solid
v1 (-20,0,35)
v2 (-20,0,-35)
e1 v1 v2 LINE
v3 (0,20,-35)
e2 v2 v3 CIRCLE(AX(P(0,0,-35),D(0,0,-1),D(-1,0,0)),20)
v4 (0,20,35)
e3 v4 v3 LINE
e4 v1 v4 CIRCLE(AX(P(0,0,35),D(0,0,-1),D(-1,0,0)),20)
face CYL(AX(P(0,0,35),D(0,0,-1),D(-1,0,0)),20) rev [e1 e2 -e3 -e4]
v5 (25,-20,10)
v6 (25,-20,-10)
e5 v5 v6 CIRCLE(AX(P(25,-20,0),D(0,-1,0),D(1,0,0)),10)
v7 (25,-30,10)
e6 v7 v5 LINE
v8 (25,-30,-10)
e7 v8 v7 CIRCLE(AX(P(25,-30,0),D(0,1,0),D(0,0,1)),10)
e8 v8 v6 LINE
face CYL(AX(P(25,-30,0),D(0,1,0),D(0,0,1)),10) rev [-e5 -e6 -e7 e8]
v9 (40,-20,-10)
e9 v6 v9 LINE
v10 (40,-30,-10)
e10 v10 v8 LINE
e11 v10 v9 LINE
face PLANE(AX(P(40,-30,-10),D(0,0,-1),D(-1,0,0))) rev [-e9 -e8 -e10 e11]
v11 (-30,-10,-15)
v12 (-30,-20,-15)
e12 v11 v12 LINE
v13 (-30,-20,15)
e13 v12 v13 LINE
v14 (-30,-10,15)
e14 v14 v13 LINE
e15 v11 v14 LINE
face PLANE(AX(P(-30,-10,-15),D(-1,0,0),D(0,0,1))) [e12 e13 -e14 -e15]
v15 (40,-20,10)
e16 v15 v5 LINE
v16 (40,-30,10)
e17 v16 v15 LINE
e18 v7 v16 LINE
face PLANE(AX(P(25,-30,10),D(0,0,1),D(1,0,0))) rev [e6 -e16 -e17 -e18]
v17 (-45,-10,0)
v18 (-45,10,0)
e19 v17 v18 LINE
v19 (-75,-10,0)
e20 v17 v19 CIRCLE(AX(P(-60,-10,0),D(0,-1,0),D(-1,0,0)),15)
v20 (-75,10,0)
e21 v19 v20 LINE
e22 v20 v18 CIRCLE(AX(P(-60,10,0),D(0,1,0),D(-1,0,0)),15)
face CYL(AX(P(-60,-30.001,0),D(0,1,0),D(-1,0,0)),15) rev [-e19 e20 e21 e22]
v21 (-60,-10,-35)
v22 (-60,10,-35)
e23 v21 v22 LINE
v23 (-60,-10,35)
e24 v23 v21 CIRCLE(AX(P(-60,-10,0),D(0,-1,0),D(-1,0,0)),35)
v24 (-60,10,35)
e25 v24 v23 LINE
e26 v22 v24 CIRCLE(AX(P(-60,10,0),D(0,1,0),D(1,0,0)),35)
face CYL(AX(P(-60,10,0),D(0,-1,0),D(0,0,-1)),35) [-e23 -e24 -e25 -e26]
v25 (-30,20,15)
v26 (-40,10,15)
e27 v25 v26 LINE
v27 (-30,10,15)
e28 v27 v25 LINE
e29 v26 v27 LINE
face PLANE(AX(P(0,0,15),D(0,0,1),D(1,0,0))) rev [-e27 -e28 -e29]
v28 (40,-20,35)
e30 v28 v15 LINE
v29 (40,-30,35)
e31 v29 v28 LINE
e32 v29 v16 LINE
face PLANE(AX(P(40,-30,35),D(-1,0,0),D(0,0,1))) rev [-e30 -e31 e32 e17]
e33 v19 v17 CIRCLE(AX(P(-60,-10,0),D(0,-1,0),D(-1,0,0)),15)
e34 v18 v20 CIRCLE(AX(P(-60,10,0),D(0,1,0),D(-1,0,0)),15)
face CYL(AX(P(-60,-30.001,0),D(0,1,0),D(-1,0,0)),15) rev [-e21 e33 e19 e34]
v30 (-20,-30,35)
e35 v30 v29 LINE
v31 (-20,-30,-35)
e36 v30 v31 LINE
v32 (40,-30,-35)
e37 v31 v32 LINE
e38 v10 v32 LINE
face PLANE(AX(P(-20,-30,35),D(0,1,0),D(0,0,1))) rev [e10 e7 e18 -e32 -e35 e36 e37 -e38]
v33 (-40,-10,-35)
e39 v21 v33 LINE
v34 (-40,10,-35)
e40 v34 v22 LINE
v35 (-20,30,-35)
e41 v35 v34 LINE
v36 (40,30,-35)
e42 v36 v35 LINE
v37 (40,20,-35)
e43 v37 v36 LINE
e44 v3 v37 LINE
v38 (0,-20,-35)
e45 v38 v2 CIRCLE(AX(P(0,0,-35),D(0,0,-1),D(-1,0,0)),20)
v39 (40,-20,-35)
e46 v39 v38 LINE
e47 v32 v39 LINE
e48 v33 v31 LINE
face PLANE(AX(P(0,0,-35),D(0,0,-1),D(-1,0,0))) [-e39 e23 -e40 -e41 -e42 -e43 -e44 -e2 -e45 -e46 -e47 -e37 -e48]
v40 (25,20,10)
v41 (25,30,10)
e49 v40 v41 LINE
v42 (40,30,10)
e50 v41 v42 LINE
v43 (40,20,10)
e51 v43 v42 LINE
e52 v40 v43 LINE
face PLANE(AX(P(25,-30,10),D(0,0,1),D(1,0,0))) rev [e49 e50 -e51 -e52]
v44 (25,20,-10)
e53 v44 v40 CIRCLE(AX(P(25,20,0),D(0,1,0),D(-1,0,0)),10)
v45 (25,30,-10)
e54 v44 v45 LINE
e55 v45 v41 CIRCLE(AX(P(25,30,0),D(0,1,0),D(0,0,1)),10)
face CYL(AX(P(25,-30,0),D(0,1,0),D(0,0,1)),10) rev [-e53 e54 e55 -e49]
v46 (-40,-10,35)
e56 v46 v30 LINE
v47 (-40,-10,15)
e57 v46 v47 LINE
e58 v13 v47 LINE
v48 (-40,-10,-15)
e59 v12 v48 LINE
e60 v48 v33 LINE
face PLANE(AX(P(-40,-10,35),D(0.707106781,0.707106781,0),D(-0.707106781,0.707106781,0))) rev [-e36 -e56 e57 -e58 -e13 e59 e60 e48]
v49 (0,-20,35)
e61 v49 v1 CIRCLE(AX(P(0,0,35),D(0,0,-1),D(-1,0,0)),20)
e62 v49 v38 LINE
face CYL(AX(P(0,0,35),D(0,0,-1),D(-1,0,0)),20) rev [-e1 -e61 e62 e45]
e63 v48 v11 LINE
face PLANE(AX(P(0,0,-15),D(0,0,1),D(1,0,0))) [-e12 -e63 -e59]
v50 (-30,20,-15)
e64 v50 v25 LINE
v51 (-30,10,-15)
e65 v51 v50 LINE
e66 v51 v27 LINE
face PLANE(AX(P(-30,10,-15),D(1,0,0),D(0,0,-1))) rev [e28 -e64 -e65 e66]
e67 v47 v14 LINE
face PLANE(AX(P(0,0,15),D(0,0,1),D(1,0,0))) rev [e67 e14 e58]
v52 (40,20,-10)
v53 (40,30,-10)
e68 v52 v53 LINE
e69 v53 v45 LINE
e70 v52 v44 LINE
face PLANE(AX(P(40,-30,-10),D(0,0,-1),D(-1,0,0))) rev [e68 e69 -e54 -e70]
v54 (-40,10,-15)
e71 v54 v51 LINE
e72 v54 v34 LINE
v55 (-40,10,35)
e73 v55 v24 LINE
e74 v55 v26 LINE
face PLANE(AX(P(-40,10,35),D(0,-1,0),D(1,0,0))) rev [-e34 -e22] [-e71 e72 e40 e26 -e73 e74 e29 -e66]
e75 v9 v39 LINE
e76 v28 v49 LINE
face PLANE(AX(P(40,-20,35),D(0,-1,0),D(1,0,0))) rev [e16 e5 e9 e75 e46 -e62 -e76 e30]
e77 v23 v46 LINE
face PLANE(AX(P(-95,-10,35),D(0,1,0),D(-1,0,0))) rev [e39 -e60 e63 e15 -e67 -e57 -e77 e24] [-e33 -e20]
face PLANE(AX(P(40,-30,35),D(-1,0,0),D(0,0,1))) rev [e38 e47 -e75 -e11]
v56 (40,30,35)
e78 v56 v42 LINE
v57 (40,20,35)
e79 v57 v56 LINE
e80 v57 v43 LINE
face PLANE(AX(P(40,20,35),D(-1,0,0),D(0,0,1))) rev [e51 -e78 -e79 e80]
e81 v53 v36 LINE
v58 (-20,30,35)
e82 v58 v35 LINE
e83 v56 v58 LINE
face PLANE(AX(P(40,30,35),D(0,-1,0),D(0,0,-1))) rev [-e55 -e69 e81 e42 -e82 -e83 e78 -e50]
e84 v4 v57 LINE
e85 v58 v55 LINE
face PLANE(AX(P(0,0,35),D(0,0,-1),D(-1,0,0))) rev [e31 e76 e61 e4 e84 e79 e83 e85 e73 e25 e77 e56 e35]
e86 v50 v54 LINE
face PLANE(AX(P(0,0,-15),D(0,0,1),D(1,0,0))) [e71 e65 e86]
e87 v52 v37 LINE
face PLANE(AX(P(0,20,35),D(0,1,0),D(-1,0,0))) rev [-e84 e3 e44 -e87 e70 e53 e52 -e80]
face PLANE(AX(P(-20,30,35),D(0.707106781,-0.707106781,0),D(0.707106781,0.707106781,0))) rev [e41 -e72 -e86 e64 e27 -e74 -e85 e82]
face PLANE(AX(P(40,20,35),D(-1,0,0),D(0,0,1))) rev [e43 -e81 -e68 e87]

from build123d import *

# Parameters (mm, degrees)
BRACKET_BODY_DEPTH      = 35
EYE_END_ROUND_RADIUS    = 35
EYE_END_ROUND_LENGTH    = 20
FORK_GAP_CUT_DEPTH      = 106.59356041
FORK_GAP_CUT_DEPTH_BACK = 106.59356041
FORK_SLOT_CUT_DEPTH     = 15
EYE_BORE_30_REACH       = 110.858
EYE_BORE_SKETCH_R       = 15


with BuildPart() as part:
    # Bracket Profile Sketch → Bracket Body (new, symmetric)
    with BuildSketch(Plane.XY):
        with BuildLine():
            Line((40, -20), (0, -20))
            ThreePointArc((0, -20), (-20, 0), (0, 20))
            Line((0, 20), (40, 20))
            Line((40, 20), (40, 30))
            Line((40, 30), (-20, 30))
            Line((-20, 30), (-40, 10))
            Line((-40, 10), (-95, 10))
            Line((-95, 10), (-95, -10))
            Line((-95, -10), (-40, -10))
            Line((-40, -10), (-20, -30))
            Line((-20, -30), (40, -30))
            Line((40, -30), (40, -20))
        make_face()
    extrude(amount=BRACKET_BODY_DEPTH, both=True)

    # Eye End Round: full round fillet: the end face becomes a half cylinder, R = half its width
    eye_end_round_face = Plane((-95, 0, 0), x_dir=(0, -1, 0), z_dir=(-1, 0, 0))  # on the end face: x along it, z out of the body
    eye_end_round_slab = eye_end_round_face.offset(-EYE_END_ROUND_RADIUS / 2) * Box(EYE_END_ROUND_LENGTH, 2 * EYE_END_ROUND_RADIUS, EYE_END_ROUND_RADIUS, mode=Mode.PRIVATE)  # the body's end, R deep
    eye_end_round_round = Plane((-60, 0, 0), x_dir=(-1, 0, 0), z_dir=(0, -1, 0)) * Cylinder(EYE_END_ROUND_RADIUS, EYE_END_ROUND_LENGTH, mode=Mode.PRIVATE)  # its axis R under the face
    add(eye_end_round_slab - eye_end_round_round, mode=Mode.SUBTRACT)

    # Fork Gap Sketch → Fork Gap Cut (cut, two sides: drawn at the far end of the back side and taken through both)
    with BuildSketch(Plane(origin=(0, 0, 0), x_dir=(1, 0, 0), z_dir=(0, 1, 0)).offset(-FORK_GAP_CUT_DEPTH_BACK)):
        with BuildLine():
            Line((40, 10), (25, 10))
            ThreePointArc((25, 10), (15, 0), (25, -10))
            Line((25, -10), (40, -10))
            Line((40, -10), (40, 10))
        make_face()
    extrude(amount=FORK_GAP_CUT_DEPTH + FORK_GAP_CUT_DEPTH_BACK, mode=Mode.SUBTRACT)

    # Fork Slot Sketch → Fork Slot Cut (cut, symmetric)
    with BuildSketch(Plane.XY):
        Polygon((-40, 10), (-30, 10), (-30, 20), align=None)
    fork_slot_cut = extrude(amount=FORK_SLOT_CUT_DEPTH, both=True, mode=Mode.SUBTRACT)

    # Eye Bore Sketch → Eye Bore _30 (cut, up to next)
    with BuildSketch(Plane(origin=(0, 10, 0), x_dir=(1, 0, 0), z_dir=(0, 1, 0)), mode=Mode.PRIVATE) as eye_bore_30_sk1:
        with Locations(Location((-60, 0, 0), (0, 0, 180))):
            Circle(EYE_BORE_SKETCH_R)
    eye_bore_30_tool1 = extrude(eye_bore_30_sk1.sketch, amount=-EYE_BORE_30_REACH, mode=Mode.PRIVATE) & part.part
    add(eye_bore_30_tool1.solids().sort_by_distance((-60, 10, 0))[0], mode=Mode.SUBTRACT)

    # Fork Slot Mirror: Fork Slot Cut across plane
    add(fork_slot_cut.mirror(Plane.ZX), mode=Mode.SUBTRACT)


solid = part.part
